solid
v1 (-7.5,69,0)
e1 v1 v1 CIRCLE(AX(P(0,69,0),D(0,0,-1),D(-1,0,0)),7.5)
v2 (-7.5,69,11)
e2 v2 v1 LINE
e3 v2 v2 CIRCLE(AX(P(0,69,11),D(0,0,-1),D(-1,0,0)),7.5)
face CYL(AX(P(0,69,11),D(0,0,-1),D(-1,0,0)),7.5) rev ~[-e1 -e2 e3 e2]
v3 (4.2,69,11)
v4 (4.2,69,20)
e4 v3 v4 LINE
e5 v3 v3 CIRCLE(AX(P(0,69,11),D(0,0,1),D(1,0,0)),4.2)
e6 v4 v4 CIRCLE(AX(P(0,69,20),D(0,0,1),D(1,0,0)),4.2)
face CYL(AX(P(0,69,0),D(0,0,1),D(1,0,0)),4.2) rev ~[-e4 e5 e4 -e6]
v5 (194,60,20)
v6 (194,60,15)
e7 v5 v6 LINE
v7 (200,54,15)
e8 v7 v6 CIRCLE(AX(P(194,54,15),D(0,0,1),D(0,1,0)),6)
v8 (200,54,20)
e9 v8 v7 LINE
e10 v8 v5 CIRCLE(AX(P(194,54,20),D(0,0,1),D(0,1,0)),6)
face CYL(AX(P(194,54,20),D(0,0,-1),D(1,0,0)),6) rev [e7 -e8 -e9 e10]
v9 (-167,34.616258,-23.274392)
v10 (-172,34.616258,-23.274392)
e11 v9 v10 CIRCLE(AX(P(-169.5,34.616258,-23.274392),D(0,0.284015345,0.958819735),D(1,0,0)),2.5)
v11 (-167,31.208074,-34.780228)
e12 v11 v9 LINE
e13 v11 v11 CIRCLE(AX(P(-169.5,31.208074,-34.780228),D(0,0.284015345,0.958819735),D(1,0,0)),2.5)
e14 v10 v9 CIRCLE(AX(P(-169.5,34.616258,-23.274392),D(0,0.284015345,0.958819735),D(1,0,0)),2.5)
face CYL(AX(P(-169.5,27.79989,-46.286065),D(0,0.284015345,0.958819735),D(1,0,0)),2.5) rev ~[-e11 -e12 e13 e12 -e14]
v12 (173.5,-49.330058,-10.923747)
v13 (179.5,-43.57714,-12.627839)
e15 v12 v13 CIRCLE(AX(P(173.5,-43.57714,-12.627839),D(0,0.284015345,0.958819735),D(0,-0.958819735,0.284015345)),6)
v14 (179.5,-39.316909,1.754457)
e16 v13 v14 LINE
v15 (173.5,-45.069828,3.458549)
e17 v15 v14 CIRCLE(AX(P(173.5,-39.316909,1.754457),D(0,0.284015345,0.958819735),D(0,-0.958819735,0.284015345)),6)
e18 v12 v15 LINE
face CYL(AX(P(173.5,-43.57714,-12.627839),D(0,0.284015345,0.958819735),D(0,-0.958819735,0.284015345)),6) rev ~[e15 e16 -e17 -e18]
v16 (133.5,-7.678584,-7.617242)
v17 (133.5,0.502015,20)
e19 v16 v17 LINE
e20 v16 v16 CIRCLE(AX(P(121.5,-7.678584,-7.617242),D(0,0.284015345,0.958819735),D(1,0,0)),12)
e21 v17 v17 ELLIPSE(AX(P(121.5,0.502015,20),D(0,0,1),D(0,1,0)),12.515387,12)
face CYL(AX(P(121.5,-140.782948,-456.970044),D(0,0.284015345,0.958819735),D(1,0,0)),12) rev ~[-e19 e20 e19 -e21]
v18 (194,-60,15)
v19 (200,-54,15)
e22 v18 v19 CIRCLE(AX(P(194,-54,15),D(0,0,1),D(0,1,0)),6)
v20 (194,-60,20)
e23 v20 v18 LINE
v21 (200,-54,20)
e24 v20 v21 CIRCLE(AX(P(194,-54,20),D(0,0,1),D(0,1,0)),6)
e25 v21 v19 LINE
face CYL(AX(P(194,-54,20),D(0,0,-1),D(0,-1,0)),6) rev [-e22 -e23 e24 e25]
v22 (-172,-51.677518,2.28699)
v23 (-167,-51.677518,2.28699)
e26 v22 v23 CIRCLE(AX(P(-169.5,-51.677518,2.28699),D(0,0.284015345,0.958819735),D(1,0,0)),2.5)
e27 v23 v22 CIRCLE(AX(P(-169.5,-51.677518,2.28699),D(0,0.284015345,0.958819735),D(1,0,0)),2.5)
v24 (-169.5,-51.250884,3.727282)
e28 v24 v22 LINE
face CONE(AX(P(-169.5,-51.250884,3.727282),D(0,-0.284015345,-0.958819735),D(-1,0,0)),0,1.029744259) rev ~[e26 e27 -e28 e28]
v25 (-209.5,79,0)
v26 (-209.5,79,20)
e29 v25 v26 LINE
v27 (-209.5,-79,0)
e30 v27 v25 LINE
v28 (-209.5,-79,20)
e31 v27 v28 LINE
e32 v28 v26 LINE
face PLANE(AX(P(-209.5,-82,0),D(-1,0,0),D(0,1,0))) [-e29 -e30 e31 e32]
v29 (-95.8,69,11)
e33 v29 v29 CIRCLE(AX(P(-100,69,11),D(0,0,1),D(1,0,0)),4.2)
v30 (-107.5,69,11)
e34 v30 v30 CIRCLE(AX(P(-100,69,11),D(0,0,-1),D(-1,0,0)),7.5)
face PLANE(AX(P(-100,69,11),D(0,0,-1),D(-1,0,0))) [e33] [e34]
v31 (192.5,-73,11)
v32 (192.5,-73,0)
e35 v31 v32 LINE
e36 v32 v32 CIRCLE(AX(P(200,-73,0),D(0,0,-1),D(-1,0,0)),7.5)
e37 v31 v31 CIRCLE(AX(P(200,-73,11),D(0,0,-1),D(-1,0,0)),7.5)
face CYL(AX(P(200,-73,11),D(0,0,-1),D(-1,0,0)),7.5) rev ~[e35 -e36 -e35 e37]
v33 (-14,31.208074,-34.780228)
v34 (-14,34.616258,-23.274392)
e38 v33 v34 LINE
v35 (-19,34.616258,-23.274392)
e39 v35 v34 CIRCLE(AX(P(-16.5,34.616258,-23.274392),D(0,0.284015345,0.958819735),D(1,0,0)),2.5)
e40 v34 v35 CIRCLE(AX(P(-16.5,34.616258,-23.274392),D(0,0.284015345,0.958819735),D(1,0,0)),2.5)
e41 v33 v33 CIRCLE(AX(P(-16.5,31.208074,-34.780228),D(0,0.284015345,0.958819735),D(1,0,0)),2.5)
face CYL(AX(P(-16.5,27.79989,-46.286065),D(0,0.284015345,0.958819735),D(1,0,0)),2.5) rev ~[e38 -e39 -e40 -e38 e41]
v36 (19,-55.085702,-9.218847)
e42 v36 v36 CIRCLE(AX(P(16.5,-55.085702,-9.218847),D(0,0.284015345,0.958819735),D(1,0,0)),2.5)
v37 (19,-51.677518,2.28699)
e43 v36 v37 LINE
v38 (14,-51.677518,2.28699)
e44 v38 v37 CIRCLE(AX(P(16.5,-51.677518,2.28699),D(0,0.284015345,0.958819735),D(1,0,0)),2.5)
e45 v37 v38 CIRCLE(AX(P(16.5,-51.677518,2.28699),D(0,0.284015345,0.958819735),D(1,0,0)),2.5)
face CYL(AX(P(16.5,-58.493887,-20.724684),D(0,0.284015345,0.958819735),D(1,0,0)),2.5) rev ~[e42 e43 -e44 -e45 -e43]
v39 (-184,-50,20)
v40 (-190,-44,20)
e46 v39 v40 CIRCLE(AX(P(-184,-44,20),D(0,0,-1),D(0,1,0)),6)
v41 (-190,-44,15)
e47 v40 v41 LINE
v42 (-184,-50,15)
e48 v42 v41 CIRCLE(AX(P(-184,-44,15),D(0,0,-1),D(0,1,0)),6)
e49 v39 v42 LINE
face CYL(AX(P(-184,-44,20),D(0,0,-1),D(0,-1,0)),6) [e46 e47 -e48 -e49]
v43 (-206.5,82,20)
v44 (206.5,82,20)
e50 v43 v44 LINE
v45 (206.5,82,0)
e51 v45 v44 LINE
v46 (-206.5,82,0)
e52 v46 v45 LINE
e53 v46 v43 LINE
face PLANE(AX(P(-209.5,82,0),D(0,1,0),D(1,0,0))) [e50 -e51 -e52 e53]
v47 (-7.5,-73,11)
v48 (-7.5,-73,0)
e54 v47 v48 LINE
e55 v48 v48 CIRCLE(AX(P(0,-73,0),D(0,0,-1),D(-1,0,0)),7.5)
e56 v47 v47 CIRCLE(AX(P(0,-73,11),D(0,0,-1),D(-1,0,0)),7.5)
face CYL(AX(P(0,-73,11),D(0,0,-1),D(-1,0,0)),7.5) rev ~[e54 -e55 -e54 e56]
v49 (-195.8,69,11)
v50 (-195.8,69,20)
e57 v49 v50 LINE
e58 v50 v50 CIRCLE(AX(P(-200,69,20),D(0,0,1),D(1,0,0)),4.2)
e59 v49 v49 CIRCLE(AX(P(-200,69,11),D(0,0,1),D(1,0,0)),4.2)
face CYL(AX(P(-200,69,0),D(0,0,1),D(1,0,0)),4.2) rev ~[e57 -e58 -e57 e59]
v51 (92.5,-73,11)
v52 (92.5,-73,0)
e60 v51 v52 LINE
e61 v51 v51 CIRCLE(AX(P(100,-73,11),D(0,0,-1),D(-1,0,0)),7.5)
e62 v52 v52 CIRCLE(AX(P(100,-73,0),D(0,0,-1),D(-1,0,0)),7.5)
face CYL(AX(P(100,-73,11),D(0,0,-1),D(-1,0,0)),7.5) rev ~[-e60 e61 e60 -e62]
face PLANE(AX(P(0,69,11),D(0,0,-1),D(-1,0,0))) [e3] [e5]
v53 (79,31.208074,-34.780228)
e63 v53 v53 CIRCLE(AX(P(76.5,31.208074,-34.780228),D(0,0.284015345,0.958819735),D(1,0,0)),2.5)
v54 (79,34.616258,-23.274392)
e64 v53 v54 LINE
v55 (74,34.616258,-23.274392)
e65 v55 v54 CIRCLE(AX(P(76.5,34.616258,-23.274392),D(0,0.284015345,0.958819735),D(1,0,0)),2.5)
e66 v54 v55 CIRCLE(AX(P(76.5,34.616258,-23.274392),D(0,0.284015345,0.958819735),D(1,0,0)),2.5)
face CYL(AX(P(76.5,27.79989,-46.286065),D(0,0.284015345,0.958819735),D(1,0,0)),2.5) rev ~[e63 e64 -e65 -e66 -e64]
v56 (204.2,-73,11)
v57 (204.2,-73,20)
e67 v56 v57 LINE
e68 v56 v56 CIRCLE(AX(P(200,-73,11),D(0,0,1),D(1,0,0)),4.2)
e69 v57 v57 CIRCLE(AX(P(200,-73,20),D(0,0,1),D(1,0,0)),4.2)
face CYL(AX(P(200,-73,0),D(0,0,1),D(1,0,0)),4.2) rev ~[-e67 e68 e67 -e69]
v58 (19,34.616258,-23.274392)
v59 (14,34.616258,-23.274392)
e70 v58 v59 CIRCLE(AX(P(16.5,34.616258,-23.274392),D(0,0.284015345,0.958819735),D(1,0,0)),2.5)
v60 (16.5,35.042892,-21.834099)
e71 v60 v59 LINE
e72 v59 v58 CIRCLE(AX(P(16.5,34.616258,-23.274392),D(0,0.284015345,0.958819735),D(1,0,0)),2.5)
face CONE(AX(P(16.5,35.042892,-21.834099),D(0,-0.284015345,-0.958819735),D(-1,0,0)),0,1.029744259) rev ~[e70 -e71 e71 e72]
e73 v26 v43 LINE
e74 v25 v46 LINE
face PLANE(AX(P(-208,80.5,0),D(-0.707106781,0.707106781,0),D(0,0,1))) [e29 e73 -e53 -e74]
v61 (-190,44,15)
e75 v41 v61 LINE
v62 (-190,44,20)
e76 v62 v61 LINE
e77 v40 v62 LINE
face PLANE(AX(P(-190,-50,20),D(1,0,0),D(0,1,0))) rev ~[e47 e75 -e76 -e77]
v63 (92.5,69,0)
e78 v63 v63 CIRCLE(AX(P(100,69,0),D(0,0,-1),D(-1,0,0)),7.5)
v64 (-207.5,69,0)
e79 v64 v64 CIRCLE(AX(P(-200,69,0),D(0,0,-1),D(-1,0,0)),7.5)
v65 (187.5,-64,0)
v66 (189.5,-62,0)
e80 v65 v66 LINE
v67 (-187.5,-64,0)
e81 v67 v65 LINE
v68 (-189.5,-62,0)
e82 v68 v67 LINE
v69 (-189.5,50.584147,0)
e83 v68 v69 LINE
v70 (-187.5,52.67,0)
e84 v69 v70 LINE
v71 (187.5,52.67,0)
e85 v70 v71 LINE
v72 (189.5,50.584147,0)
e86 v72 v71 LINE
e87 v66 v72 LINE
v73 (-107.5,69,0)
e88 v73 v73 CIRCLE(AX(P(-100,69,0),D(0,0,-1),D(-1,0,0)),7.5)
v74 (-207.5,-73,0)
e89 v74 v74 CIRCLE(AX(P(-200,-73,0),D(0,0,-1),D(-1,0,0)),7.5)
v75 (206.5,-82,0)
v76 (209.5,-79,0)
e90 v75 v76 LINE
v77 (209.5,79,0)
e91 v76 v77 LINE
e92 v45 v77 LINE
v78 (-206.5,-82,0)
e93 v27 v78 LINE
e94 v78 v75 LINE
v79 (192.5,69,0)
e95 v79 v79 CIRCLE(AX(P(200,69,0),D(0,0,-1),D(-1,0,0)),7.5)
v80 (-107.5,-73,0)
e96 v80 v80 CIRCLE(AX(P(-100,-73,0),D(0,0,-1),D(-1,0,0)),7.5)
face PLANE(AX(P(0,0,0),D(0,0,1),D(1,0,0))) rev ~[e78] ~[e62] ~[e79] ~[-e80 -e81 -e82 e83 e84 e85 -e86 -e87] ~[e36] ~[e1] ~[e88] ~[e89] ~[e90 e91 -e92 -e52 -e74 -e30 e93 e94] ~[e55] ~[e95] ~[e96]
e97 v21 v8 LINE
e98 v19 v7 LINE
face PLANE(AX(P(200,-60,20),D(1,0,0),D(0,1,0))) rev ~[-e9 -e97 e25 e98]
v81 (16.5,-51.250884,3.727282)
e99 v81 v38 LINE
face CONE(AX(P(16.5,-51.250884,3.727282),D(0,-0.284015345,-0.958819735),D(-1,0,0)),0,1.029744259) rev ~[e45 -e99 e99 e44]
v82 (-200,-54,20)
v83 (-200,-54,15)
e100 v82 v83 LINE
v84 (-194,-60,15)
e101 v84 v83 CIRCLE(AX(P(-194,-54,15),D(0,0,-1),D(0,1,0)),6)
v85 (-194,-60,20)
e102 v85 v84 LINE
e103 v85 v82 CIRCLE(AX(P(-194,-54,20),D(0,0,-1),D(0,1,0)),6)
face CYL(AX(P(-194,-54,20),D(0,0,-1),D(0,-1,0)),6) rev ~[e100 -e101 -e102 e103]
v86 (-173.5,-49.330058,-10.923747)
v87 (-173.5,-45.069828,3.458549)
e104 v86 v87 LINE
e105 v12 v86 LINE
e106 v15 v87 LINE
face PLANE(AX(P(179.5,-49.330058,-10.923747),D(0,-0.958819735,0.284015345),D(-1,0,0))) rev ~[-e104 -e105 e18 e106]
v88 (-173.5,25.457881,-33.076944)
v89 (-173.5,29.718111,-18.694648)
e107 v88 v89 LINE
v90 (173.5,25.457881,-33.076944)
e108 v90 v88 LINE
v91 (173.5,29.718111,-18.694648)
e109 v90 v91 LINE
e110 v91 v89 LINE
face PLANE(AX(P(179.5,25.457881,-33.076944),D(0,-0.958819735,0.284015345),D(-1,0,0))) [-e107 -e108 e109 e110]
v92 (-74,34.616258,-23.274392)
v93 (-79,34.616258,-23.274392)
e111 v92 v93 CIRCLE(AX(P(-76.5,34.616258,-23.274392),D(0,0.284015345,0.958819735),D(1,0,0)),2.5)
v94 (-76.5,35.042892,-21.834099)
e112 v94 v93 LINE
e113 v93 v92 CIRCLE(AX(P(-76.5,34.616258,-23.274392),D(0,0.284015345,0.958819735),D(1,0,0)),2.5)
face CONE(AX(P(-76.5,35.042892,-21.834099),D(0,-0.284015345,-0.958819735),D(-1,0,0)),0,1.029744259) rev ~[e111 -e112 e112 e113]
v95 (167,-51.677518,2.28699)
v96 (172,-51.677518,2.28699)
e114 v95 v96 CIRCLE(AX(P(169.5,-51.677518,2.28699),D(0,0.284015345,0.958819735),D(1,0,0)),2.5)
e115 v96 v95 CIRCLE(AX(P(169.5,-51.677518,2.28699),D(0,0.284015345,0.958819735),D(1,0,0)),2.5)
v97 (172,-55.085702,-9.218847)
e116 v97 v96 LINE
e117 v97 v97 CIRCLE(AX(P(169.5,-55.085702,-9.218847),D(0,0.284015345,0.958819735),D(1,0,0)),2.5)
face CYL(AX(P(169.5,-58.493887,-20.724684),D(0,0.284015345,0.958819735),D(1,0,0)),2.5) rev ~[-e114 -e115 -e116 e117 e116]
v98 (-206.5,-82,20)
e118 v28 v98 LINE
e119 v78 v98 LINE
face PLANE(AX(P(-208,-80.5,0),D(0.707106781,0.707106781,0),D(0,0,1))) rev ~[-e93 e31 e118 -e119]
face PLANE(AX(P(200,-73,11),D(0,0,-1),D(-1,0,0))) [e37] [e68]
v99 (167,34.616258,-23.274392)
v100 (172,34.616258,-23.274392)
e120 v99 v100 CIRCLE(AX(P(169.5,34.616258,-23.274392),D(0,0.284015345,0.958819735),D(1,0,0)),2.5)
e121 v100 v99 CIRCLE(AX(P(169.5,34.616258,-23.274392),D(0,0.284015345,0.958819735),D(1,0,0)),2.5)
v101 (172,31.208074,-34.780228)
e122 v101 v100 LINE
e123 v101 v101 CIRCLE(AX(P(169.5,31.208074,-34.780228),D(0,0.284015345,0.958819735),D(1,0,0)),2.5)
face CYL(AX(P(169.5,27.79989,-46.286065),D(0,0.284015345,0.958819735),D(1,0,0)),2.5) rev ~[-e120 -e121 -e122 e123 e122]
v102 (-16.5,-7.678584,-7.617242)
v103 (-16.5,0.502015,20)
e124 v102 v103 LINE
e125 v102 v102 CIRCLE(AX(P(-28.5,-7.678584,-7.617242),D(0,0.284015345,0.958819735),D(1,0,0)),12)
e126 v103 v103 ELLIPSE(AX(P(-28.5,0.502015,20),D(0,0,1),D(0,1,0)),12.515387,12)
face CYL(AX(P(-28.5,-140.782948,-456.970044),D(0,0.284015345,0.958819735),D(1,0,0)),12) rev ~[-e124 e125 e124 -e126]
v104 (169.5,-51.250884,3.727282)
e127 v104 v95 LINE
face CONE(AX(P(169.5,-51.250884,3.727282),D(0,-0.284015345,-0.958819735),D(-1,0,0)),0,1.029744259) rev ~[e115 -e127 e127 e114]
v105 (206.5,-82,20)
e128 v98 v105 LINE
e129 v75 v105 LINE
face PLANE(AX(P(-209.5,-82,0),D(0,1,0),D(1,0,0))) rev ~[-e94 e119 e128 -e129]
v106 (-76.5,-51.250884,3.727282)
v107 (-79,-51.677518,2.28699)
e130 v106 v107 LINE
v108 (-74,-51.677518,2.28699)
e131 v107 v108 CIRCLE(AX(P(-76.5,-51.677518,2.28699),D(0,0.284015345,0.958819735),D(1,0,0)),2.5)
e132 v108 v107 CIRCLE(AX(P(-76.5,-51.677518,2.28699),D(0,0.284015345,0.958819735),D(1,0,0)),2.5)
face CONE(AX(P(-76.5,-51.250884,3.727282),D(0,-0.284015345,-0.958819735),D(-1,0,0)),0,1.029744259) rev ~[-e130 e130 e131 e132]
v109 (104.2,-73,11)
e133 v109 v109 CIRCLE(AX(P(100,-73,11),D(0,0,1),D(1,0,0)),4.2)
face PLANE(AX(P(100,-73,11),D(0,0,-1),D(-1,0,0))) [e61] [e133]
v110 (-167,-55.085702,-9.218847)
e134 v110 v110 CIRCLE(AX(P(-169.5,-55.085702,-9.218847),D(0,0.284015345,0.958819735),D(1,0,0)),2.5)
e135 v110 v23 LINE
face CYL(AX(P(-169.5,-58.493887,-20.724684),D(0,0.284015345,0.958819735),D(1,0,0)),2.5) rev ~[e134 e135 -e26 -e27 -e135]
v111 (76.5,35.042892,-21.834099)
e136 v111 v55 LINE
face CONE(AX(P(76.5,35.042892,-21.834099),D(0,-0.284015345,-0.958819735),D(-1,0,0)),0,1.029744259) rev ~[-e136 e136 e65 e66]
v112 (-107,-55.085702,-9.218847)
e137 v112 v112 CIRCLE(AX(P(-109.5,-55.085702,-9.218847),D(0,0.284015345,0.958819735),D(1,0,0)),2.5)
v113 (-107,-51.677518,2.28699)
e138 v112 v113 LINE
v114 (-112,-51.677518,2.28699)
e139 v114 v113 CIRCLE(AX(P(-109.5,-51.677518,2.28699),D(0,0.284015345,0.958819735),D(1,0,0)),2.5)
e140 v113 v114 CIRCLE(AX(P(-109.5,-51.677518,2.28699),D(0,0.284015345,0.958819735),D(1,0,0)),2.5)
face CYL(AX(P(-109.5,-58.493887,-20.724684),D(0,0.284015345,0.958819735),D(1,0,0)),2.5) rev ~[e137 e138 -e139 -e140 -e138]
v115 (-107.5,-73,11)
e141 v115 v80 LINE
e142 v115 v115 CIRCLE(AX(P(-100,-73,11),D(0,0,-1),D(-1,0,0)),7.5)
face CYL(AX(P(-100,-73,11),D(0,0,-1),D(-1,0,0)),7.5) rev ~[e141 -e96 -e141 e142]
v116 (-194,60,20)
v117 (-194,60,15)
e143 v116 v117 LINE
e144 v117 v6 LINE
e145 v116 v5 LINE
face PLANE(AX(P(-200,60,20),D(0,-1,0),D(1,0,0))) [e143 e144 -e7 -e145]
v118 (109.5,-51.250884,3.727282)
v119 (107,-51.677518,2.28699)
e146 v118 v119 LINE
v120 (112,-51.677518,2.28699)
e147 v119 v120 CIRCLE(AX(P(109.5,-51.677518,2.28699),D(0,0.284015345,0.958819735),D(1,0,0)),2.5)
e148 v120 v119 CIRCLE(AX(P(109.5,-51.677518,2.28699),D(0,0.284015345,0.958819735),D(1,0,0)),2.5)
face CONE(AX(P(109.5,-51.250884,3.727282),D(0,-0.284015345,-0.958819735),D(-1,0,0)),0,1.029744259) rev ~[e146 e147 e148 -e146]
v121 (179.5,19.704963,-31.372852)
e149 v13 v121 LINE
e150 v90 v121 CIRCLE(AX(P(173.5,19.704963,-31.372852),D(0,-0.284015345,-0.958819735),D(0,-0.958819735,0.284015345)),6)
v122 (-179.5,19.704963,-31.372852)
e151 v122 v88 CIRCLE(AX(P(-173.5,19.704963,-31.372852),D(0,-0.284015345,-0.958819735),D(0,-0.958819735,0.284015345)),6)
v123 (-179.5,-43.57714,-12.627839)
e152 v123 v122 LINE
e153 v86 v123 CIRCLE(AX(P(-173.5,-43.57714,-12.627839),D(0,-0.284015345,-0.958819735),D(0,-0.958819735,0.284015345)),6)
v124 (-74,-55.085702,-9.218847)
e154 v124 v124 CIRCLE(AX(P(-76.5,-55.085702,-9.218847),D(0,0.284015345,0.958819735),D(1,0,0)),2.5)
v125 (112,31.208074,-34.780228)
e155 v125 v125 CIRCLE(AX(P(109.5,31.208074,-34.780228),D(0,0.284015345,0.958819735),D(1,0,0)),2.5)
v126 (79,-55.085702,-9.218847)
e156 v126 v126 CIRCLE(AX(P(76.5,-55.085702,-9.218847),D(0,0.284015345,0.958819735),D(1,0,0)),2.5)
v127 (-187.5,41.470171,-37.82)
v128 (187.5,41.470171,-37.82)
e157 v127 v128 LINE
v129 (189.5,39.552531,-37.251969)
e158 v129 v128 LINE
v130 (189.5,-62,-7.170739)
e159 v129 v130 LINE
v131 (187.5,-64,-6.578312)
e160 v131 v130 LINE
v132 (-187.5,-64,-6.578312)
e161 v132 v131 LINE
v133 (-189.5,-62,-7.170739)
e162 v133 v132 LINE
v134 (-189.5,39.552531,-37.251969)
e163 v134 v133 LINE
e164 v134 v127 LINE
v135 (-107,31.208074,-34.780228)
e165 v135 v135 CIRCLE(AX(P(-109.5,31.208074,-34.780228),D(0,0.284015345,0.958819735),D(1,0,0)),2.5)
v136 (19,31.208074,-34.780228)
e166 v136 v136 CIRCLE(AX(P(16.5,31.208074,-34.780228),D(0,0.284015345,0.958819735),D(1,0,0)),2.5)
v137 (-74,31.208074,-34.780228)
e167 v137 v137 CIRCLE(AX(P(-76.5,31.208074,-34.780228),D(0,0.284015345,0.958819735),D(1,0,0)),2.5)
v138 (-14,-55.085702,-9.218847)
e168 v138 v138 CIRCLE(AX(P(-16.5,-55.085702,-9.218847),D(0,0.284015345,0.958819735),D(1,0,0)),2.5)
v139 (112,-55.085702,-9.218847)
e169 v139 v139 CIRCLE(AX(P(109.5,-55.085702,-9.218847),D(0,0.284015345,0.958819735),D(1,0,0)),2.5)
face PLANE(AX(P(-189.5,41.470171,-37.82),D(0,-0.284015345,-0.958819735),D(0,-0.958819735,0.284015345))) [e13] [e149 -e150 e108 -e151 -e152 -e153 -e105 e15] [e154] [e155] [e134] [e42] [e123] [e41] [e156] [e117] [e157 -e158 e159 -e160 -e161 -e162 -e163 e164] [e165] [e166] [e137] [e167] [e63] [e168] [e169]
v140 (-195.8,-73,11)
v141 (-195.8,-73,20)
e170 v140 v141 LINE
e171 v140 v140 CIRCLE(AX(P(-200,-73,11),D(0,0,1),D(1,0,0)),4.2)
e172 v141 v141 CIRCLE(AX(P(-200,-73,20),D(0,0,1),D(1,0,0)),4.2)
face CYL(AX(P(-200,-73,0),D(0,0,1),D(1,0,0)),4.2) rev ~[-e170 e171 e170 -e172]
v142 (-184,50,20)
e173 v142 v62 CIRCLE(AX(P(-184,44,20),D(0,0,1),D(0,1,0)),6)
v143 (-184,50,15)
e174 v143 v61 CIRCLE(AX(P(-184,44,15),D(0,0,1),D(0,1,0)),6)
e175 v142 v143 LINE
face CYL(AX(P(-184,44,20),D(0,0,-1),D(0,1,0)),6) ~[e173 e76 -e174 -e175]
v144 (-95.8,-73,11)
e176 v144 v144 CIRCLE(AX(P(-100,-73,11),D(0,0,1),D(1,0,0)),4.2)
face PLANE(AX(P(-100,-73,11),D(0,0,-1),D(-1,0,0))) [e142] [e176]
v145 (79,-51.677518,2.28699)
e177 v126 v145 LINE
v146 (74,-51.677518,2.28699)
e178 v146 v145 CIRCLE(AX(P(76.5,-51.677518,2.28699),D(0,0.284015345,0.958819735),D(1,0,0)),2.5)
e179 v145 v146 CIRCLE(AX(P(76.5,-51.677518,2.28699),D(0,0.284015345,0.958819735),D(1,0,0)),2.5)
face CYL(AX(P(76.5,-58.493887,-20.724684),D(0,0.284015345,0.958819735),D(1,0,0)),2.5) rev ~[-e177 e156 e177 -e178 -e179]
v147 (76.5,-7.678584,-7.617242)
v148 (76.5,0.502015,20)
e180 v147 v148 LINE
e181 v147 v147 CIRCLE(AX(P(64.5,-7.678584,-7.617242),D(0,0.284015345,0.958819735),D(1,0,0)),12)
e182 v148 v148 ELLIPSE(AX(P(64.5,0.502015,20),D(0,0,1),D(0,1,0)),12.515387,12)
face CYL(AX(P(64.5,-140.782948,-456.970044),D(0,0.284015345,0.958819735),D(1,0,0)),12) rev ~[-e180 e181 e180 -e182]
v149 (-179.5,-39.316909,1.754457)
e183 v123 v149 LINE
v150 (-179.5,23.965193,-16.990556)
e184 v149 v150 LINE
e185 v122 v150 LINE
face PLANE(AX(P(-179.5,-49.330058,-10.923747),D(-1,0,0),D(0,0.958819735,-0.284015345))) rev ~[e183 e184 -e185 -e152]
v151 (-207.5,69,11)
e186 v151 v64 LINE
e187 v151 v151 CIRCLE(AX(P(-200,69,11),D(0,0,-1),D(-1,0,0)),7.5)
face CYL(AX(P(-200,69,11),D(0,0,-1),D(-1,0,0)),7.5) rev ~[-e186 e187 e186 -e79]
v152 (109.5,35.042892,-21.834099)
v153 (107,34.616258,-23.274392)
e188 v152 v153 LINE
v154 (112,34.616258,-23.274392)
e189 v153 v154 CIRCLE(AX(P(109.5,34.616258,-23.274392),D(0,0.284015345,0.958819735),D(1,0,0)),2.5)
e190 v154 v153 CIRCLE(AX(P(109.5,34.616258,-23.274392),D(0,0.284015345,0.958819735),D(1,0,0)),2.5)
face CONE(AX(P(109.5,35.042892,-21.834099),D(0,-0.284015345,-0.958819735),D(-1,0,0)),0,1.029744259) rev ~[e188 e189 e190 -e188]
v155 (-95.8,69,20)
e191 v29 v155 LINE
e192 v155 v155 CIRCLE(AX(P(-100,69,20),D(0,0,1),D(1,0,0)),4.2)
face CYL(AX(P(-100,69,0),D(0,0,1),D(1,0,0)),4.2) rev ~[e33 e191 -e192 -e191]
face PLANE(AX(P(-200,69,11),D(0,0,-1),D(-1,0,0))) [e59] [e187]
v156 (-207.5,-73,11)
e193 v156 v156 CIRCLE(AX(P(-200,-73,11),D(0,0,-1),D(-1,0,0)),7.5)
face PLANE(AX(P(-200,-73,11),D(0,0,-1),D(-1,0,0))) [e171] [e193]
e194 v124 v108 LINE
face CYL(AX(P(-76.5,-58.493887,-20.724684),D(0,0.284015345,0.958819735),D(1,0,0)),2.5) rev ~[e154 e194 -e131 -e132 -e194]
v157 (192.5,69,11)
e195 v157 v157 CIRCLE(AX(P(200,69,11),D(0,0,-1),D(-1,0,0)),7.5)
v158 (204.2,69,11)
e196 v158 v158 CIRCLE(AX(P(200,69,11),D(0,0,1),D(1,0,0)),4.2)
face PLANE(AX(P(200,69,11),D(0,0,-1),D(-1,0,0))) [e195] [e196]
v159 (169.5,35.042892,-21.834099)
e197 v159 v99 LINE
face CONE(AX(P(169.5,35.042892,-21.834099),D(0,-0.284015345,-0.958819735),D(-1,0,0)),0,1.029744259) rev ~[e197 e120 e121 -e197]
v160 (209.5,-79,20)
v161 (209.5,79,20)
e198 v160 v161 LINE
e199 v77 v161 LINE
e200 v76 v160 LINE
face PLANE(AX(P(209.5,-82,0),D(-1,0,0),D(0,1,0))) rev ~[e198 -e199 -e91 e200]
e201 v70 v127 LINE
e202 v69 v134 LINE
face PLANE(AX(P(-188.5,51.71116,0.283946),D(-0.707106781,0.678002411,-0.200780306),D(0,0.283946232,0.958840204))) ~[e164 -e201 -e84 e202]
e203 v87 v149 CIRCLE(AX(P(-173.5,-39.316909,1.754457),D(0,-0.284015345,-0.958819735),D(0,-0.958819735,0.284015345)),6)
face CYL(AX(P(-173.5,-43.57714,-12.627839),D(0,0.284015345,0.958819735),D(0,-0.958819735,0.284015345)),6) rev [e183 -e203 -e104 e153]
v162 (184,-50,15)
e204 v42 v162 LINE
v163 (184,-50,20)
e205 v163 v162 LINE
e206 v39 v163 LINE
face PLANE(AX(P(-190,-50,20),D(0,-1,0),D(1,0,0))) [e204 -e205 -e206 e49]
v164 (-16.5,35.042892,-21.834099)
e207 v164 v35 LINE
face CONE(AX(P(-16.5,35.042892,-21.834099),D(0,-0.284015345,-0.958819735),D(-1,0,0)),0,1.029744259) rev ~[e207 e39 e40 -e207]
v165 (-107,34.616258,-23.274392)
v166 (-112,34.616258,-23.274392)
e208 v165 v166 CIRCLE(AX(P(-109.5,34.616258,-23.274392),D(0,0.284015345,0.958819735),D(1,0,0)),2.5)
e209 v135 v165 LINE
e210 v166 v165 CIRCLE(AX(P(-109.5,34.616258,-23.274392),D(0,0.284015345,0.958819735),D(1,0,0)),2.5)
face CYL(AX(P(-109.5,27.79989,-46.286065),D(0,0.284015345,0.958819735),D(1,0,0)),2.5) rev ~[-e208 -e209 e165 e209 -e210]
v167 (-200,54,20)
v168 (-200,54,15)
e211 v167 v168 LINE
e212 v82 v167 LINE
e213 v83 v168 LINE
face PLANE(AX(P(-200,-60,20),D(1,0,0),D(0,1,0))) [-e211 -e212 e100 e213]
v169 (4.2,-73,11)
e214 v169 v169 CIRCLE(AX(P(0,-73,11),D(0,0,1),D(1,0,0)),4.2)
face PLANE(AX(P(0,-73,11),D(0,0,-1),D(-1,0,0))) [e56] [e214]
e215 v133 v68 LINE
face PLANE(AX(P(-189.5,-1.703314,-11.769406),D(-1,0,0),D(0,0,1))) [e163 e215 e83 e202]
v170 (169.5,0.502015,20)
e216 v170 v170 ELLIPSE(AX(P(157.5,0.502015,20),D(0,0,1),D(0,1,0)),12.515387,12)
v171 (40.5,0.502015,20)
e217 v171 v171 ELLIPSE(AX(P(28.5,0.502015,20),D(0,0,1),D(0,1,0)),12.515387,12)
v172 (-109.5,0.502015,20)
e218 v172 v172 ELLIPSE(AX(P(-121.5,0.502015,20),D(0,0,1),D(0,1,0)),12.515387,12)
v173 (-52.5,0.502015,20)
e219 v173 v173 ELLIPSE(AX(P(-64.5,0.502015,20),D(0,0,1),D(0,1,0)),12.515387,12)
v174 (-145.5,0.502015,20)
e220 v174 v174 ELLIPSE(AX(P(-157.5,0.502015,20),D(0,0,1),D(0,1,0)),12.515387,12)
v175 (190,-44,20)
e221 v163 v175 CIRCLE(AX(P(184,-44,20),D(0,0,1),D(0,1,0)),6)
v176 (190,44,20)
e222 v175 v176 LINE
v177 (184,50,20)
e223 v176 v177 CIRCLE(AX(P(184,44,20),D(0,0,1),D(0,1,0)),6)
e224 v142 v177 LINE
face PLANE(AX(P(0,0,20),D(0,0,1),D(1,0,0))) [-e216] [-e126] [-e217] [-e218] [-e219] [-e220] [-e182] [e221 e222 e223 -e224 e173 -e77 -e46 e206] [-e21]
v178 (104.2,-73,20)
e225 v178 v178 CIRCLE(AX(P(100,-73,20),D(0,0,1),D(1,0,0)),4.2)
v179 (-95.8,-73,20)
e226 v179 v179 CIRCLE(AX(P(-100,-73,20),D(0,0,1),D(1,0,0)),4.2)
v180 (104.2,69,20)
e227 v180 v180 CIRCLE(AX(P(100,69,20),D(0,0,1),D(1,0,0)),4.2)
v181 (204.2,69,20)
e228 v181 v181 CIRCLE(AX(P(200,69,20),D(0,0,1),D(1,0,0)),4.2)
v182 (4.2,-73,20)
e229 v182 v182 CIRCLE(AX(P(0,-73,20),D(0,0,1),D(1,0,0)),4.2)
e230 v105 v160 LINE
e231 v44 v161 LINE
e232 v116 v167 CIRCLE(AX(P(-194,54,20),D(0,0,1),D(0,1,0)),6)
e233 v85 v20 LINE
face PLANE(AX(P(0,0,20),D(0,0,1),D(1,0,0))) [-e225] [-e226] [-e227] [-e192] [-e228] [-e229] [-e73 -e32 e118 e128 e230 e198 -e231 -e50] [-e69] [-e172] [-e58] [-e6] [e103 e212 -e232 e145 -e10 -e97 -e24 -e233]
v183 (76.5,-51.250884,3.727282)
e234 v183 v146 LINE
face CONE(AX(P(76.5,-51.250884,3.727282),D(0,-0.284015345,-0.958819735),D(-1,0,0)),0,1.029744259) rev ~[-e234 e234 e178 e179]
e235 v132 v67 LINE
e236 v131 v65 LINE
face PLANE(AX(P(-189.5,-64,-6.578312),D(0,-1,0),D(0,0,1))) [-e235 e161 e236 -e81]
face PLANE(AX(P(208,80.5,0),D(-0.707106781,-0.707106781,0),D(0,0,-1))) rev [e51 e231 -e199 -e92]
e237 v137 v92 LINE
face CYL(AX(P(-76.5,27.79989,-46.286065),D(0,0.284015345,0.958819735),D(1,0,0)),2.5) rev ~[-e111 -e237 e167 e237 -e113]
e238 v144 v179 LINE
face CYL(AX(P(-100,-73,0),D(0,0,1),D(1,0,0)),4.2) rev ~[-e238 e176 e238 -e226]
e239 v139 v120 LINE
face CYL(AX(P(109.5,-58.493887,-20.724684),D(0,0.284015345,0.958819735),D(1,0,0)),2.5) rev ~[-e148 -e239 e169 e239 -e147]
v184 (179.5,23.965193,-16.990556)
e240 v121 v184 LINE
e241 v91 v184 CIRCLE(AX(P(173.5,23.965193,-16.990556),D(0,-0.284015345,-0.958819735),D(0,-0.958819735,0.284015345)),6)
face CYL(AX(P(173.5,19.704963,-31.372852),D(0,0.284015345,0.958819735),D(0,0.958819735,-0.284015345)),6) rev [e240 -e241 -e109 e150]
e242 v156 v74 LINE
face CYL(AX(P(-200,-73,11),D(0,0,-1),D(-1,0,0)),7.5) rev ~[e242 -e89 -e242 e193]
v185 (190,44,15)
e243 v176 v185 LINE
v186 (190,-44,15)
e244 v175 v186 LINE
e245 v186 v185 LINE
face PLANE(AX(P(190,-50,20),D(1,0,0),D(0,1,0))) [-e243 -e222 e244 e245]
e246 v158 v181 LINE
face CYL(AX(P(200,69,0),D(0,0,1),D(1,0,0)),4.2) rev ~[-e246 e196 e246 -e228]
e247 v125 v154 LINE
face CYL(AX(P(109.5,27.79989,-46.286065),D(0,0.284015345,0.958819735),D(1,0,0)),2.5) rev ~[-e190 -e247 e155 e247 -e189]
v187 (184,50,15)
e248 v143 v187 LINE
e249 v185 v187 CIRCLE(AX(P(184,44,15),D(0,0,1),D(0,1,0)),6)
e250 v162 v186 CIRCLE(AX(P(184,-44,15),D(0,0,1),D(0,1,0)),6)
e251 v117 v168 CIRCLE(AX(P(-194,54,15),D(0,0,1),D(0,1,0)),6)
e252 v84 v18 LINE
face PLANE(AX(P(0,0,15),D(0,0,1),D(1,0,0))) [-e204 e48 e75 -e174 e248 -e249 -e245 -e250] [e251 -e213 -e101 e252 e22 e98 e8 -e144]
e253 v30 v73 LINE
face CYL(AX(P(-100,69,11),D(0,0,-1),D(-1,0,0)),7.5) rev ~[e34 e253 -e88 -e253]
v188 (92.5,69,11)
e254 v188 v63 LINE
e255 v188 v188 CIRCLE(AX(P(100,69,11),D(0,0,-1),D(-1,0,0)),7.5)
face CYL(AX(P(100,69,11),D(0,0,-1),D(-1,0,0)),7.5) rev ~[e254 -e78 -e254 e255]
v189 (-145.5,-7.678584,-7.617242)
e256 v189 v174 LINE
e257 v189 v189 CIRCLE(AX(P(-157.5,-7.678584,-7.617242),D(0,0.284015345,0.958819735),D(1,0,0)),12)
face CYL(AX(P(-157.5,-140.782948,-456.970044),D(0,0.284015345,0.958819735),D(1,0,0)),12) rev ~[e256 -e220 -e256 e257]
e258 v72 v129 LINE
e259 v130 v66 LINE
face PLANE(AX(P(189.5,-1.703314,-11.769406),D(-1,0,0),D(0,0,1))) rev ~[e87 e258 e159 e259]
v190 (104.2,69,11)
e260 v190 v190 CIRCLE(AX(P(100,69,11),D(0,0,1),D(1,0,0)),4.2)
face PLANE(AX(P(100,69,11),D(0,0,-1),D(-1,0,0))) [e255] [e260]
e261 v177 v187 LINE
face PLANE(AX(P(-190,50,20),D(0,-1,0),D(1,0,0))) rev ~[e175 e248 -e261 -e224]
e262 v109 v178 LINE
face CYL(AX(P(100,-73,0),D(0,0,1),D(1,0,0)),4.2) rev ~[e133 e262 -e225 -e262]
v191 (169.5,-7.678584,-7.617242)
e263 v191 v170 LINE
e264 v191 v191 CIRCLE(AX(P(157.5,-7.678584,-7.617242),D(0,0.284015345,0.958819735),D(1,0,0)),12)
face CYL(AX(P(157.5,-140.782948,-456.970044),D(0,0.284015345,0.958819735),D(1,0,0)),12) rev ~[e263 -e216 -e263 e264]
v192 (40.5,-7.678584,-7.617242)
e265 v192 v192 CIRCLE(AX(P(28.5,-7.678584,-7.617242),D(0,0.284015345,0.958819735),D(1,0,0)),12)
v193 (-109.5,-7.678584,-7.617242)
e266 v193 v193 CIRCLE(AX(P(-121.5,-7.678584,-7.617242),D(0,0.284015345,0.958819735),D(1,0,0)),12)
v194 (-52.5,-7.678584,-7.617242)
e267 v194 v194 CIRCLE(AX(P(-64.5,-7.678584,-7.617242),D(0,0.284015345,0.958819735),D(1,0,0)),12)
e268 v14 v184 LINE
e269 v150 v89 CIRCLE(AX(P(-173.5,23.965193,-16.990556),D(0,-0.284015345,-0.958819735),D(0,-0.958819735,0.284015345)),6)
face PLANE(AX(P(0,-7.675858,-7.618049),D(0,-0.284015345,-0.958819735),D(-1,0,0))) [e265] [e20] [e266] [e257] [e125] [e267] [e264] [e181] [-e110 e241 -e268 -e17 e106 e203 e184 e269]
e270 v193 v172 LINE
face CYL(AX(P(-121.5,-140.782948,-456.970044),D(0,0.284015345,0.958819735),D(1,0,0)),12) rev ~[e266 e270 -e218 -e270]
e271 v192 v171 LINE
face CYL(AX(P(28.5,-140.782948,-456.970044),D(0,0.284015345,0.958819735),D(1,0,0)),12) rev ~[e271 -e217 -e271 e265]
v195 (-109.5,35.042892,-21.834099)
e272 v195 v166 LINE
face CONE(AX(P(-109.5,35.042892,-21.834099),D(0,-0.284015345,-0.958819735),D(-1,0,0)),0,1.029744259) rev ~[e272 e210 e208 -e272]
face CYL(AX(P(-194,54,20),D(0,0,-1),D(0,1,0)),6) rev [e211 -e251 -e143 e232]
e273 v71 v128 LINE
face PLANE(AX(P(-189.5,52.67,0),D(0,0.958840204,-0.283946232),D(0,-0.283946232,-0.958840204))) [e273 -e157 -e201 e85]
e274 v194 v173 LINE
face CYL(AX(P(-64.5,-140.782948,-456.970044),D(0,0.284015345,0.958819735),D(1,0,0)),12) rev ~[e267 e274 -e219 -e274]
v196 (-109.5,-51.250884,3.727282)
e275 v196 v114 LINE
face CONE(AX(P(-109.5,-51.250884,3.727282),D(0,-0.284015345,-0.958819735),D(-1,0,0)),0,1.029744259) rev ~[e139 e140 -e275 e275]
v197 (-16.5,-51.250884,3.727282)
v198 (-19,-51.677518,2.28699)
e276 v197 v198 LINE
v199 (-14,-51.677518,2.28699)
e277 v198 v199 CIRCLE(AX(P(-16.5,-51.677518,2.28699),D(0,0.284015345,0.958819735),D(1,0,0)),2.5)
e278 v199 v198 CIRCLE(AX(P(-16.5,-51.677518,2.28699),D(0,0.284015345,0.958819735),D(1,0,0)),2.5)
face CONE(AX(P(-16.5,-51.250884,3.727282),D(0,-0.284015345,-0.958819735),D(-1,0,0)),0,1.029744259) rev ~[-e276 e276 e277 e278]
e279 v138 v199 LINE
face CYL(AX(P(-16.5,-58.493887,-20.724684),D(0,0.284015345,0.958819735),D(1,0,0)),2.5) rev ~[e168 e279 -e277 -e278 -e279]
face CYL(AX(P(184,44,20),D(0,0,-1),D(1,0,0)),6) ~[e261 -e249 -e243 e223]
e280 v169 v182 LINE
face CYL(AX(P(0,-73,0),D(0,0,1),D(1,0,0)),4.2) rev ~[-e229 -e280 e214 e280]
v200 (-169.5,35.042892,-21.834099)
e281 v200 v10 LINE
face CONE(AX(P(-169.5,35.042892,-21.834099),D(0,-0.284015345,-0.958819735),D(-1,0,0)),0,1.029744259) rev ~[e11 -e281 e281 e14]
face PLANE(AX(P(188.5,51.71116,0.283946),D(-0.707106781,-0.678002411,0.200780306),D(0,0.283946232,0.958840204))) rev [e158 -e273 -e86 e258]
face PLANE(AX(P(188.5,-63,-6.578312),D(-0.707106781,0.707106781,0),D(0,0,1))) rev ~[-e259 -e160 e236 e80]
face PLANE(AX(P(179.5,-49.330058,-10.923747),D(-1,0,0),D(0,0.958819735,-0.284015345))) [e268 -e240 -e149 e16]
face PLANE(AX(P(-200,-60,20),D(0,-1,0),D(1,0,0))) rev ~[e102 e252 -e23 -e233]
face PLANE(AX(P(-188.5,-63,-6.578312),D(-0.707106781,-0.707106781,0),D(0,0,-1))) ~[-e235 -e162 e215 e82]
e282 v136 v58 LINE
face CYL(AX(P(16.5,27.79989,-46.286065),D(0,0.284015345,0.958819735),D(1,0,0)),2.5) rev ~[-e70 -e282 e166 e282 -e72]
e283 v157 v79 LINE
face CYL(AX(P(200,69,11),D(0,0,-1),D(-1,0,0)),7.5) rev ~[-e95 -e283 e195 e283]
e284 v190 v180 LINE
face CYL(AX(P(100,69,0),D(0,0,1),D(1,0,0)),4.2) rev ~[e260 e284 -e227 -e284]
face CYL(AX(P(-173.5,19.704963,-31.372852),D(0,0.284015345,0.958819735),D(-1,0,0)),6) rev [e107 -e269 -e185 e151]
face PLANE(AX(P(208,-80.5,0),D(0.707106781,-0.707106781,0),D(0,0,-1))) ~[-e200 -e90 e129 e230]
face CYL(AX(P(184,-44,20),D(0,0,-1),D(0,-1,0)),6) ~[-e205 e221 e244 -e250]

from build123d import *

# Parameters (mm, degrees)
SKETCH1_W             = 419
SKETCH1_H             = 164
BOSS_EXTRUDE1_DEPTH   = 20
SKETCH2_W             = 400
SKETCH2_H             = 120
SKETCH2_W_2           = 380
SKETCH2_H_2           = 100
CUT_EXTRUDE1_DEPTH    = 5
FILLET1_R             = 6
CHAMFER1_SIZE         = 3
HOLE1_D               = 8.4
HOLE1_CBORE_D         = 15
HOLE1_CBORE_DEPTH     = 11
BOSS_EXTRUDE2_DEPTH   = 379
CHAMFER2_SIZE         = 2
HOLE2_D               = 24
M6_TAPPED_HOLE1_D     = 5
M6_TAPPED_HOLE1_DEPTH = 12
M6_TAPPED_HOLE1_TIP   = 1.502151548
SKETCH12_W            = 359
SKETCH12_H            = 78
CUT_EXTRUDE2_DEPTH    = 15
FILLET2_R             = 6


with BuildPart() as part:
    # Sketch1 → Boss-Extrude1 (new body)
    with BuildSketch(Plane.XY):
        Rectangle(SKETCH1_W, SKETCH1_H)
    extrude(amount=BOSS_EXTRUDE1_DEPTH)

    # Sketch2 → Cut-Extrude1 (cut)
    with BuildSketch(Plane.XY.offset(20)):
        Rectangle(SKETCH2_W, SKETCH2_H)
        Rectangle(SKETCH2_W_2, SKETCH2_H_2, mode=Mode.SUBTRACT)
    extrude(amount=-CUT_EXTRUDE1_DEPTH, mode=Mode.SUBTRACT)

    # Fillet1
    fillet1_edges = [part.edges().sort_by_distance(p)[0] for p in [
        (200, 60, 17.5),
        (200, -60, 17.5),
        (-200, -60, 17.5),
        (-200, 60, 17.5),
        (190, -50, 17.5),
        (-190, -50, 17.5),
        (-190, 50, 17.5),
        (190, 50, 17.5),
    ]]
    fillet(fillet1_edges, radius=FILLET1_R)

    # Chamfer1
    chamfer1_edges = [part.edges().sort_by_distance(p)[0] for p in [
        (209.5, -82, 10),
        (-209.5, -82, 10),
        (-209.5, 82, 10),
        (209.5, 82, 10),
    ]]
    chamfer(chamfer1_edges, length=CHAMFER1_SIZE)

    # Hole1 (through all)
    with Locations(Plane(origin=(0, 0, 0), x_dir=(-1, 0, 0), z_dir=(0, 0, -1))):
        with Locations((-200, 69), (-200, -73), (-100, -73), (0, -73), (100, -73), (200, -73), (200, 69), (100, 69), (0, 69), (-100, 69)):
            CounterBoreHole(HOLE1_D / 2, HOLE1_CBORE_D / 2, HOLE1_CBORE_DEPTH)

    # Sketch6 → Boss-Extrude2 (add)
    with BuildSketch(Plane.ZY.offset(189.5)):
        Polygon((0, 52.67), (-37.82, 41.470170836), (-6.578312083, -64), (0, -64), align=None)
    extrude(amount=-BOSS_EXTRUDE2_DEPTH)

    # Chamfer2
    chamfer2_edges = [part.edges().sort_by_distance(p)[0] for p in [
        (189.5, -64, -3.289156041),
        (189.5, 47.070085418, -18.91),
        (-189.5, 47.070085418, -18.91),
        (-189.5, -64, -3.289156041),
    ]]
    chamfer(chamfer2_edges, length=CHAMFER2_SIZE)

    # Hole2 (through all)
    with Locations(Plane(origin=(0, -6.953944598, -23.476123527), x_dir=(-1, 0, 0), z_dir=(0, -0.2840153447039166, -0.9588197348681949))):
        with Locations((157.5, -5.198964564), (121.5, -5.198964564), (64.5, -5.198964564), (28.5, -5.198964564), (-28.5, -5.198964564), (-64.5, -5.198964564), (-121.5, -5.198964564), (-157.5, -5.198964564)):
            Hole(HOLE2_D / 2)

    # M6 Tapped Hole1
    with Locations(Plane(origin=(0, -6.953944598, -23.476123527), x_dir=(-1, 0, 0), z_dir=(0, -0.2840153447039166, -0.9588197348681949))):
        with Locations((-169.5, 39.801035436), (-109.5, 39.801035436), (-76.5, 39.801035436), (-16.5, 39.801035436), (16.5, 39.801035436), (76.5, 39.801035436), (109.5, 39.801035436), (169.5, 39.801035436), (169.5, -50.198964564), (109.5, -50.198964564), (76.5, -50.198964564), (16.5, -50.198964564), (-16.5, -50.198964564), (-76.5, -50.198964564), (-109.5, -50.198964564), (-169.5, -50.198964564)):
            Hole(M6_TAPPED_HOLE1_D / 2, depth=M6_TAPPED_HOLE1_DEPTH)
            with Locations((0, 0, -(M6_TAPPED_HOLE1_DEPTH + M6_TAPPED_HOLE1_TIP / 2))):  # 118° drill point
                Cone(0, M6_TAPPED_HOLE1_D / 2, M6_TAPPED_HOLE1_TIP, mode=Mode.SUBTRACT)

    # Sketch12 → Cut-Extrude2 (cut)
    with BuildSketch(Plane(origin=(0, -6.953944598, -23.476123527), x_dir=(-1, 0, 0), z_dir=(0, -0.2840153447039166, -0.9588197348681949))):
        with Locations((0, -5.196121458)):
            Rectangle(SKETCH12_W, SKETCH12_H)
    extrude(amount=-CUT_EXTRUDE2_DEPTH, mode=Mode.SUBTRACT)

    # Fillet2
    fillet2_edges = [part.edges().sort_by_distance(p)[0] for p in [
        (179.5, -47.199942971, -3.732598845),
        (179.5, 27.587996348, -25.885795732),
        (-179.5, 27.587996348, -25.885795732),
        (-179.5, -47.199942971, -3.732598845),
    ]]
    fillet(fillet2_edges, radius=FILLET2_R)


solid = part.part
